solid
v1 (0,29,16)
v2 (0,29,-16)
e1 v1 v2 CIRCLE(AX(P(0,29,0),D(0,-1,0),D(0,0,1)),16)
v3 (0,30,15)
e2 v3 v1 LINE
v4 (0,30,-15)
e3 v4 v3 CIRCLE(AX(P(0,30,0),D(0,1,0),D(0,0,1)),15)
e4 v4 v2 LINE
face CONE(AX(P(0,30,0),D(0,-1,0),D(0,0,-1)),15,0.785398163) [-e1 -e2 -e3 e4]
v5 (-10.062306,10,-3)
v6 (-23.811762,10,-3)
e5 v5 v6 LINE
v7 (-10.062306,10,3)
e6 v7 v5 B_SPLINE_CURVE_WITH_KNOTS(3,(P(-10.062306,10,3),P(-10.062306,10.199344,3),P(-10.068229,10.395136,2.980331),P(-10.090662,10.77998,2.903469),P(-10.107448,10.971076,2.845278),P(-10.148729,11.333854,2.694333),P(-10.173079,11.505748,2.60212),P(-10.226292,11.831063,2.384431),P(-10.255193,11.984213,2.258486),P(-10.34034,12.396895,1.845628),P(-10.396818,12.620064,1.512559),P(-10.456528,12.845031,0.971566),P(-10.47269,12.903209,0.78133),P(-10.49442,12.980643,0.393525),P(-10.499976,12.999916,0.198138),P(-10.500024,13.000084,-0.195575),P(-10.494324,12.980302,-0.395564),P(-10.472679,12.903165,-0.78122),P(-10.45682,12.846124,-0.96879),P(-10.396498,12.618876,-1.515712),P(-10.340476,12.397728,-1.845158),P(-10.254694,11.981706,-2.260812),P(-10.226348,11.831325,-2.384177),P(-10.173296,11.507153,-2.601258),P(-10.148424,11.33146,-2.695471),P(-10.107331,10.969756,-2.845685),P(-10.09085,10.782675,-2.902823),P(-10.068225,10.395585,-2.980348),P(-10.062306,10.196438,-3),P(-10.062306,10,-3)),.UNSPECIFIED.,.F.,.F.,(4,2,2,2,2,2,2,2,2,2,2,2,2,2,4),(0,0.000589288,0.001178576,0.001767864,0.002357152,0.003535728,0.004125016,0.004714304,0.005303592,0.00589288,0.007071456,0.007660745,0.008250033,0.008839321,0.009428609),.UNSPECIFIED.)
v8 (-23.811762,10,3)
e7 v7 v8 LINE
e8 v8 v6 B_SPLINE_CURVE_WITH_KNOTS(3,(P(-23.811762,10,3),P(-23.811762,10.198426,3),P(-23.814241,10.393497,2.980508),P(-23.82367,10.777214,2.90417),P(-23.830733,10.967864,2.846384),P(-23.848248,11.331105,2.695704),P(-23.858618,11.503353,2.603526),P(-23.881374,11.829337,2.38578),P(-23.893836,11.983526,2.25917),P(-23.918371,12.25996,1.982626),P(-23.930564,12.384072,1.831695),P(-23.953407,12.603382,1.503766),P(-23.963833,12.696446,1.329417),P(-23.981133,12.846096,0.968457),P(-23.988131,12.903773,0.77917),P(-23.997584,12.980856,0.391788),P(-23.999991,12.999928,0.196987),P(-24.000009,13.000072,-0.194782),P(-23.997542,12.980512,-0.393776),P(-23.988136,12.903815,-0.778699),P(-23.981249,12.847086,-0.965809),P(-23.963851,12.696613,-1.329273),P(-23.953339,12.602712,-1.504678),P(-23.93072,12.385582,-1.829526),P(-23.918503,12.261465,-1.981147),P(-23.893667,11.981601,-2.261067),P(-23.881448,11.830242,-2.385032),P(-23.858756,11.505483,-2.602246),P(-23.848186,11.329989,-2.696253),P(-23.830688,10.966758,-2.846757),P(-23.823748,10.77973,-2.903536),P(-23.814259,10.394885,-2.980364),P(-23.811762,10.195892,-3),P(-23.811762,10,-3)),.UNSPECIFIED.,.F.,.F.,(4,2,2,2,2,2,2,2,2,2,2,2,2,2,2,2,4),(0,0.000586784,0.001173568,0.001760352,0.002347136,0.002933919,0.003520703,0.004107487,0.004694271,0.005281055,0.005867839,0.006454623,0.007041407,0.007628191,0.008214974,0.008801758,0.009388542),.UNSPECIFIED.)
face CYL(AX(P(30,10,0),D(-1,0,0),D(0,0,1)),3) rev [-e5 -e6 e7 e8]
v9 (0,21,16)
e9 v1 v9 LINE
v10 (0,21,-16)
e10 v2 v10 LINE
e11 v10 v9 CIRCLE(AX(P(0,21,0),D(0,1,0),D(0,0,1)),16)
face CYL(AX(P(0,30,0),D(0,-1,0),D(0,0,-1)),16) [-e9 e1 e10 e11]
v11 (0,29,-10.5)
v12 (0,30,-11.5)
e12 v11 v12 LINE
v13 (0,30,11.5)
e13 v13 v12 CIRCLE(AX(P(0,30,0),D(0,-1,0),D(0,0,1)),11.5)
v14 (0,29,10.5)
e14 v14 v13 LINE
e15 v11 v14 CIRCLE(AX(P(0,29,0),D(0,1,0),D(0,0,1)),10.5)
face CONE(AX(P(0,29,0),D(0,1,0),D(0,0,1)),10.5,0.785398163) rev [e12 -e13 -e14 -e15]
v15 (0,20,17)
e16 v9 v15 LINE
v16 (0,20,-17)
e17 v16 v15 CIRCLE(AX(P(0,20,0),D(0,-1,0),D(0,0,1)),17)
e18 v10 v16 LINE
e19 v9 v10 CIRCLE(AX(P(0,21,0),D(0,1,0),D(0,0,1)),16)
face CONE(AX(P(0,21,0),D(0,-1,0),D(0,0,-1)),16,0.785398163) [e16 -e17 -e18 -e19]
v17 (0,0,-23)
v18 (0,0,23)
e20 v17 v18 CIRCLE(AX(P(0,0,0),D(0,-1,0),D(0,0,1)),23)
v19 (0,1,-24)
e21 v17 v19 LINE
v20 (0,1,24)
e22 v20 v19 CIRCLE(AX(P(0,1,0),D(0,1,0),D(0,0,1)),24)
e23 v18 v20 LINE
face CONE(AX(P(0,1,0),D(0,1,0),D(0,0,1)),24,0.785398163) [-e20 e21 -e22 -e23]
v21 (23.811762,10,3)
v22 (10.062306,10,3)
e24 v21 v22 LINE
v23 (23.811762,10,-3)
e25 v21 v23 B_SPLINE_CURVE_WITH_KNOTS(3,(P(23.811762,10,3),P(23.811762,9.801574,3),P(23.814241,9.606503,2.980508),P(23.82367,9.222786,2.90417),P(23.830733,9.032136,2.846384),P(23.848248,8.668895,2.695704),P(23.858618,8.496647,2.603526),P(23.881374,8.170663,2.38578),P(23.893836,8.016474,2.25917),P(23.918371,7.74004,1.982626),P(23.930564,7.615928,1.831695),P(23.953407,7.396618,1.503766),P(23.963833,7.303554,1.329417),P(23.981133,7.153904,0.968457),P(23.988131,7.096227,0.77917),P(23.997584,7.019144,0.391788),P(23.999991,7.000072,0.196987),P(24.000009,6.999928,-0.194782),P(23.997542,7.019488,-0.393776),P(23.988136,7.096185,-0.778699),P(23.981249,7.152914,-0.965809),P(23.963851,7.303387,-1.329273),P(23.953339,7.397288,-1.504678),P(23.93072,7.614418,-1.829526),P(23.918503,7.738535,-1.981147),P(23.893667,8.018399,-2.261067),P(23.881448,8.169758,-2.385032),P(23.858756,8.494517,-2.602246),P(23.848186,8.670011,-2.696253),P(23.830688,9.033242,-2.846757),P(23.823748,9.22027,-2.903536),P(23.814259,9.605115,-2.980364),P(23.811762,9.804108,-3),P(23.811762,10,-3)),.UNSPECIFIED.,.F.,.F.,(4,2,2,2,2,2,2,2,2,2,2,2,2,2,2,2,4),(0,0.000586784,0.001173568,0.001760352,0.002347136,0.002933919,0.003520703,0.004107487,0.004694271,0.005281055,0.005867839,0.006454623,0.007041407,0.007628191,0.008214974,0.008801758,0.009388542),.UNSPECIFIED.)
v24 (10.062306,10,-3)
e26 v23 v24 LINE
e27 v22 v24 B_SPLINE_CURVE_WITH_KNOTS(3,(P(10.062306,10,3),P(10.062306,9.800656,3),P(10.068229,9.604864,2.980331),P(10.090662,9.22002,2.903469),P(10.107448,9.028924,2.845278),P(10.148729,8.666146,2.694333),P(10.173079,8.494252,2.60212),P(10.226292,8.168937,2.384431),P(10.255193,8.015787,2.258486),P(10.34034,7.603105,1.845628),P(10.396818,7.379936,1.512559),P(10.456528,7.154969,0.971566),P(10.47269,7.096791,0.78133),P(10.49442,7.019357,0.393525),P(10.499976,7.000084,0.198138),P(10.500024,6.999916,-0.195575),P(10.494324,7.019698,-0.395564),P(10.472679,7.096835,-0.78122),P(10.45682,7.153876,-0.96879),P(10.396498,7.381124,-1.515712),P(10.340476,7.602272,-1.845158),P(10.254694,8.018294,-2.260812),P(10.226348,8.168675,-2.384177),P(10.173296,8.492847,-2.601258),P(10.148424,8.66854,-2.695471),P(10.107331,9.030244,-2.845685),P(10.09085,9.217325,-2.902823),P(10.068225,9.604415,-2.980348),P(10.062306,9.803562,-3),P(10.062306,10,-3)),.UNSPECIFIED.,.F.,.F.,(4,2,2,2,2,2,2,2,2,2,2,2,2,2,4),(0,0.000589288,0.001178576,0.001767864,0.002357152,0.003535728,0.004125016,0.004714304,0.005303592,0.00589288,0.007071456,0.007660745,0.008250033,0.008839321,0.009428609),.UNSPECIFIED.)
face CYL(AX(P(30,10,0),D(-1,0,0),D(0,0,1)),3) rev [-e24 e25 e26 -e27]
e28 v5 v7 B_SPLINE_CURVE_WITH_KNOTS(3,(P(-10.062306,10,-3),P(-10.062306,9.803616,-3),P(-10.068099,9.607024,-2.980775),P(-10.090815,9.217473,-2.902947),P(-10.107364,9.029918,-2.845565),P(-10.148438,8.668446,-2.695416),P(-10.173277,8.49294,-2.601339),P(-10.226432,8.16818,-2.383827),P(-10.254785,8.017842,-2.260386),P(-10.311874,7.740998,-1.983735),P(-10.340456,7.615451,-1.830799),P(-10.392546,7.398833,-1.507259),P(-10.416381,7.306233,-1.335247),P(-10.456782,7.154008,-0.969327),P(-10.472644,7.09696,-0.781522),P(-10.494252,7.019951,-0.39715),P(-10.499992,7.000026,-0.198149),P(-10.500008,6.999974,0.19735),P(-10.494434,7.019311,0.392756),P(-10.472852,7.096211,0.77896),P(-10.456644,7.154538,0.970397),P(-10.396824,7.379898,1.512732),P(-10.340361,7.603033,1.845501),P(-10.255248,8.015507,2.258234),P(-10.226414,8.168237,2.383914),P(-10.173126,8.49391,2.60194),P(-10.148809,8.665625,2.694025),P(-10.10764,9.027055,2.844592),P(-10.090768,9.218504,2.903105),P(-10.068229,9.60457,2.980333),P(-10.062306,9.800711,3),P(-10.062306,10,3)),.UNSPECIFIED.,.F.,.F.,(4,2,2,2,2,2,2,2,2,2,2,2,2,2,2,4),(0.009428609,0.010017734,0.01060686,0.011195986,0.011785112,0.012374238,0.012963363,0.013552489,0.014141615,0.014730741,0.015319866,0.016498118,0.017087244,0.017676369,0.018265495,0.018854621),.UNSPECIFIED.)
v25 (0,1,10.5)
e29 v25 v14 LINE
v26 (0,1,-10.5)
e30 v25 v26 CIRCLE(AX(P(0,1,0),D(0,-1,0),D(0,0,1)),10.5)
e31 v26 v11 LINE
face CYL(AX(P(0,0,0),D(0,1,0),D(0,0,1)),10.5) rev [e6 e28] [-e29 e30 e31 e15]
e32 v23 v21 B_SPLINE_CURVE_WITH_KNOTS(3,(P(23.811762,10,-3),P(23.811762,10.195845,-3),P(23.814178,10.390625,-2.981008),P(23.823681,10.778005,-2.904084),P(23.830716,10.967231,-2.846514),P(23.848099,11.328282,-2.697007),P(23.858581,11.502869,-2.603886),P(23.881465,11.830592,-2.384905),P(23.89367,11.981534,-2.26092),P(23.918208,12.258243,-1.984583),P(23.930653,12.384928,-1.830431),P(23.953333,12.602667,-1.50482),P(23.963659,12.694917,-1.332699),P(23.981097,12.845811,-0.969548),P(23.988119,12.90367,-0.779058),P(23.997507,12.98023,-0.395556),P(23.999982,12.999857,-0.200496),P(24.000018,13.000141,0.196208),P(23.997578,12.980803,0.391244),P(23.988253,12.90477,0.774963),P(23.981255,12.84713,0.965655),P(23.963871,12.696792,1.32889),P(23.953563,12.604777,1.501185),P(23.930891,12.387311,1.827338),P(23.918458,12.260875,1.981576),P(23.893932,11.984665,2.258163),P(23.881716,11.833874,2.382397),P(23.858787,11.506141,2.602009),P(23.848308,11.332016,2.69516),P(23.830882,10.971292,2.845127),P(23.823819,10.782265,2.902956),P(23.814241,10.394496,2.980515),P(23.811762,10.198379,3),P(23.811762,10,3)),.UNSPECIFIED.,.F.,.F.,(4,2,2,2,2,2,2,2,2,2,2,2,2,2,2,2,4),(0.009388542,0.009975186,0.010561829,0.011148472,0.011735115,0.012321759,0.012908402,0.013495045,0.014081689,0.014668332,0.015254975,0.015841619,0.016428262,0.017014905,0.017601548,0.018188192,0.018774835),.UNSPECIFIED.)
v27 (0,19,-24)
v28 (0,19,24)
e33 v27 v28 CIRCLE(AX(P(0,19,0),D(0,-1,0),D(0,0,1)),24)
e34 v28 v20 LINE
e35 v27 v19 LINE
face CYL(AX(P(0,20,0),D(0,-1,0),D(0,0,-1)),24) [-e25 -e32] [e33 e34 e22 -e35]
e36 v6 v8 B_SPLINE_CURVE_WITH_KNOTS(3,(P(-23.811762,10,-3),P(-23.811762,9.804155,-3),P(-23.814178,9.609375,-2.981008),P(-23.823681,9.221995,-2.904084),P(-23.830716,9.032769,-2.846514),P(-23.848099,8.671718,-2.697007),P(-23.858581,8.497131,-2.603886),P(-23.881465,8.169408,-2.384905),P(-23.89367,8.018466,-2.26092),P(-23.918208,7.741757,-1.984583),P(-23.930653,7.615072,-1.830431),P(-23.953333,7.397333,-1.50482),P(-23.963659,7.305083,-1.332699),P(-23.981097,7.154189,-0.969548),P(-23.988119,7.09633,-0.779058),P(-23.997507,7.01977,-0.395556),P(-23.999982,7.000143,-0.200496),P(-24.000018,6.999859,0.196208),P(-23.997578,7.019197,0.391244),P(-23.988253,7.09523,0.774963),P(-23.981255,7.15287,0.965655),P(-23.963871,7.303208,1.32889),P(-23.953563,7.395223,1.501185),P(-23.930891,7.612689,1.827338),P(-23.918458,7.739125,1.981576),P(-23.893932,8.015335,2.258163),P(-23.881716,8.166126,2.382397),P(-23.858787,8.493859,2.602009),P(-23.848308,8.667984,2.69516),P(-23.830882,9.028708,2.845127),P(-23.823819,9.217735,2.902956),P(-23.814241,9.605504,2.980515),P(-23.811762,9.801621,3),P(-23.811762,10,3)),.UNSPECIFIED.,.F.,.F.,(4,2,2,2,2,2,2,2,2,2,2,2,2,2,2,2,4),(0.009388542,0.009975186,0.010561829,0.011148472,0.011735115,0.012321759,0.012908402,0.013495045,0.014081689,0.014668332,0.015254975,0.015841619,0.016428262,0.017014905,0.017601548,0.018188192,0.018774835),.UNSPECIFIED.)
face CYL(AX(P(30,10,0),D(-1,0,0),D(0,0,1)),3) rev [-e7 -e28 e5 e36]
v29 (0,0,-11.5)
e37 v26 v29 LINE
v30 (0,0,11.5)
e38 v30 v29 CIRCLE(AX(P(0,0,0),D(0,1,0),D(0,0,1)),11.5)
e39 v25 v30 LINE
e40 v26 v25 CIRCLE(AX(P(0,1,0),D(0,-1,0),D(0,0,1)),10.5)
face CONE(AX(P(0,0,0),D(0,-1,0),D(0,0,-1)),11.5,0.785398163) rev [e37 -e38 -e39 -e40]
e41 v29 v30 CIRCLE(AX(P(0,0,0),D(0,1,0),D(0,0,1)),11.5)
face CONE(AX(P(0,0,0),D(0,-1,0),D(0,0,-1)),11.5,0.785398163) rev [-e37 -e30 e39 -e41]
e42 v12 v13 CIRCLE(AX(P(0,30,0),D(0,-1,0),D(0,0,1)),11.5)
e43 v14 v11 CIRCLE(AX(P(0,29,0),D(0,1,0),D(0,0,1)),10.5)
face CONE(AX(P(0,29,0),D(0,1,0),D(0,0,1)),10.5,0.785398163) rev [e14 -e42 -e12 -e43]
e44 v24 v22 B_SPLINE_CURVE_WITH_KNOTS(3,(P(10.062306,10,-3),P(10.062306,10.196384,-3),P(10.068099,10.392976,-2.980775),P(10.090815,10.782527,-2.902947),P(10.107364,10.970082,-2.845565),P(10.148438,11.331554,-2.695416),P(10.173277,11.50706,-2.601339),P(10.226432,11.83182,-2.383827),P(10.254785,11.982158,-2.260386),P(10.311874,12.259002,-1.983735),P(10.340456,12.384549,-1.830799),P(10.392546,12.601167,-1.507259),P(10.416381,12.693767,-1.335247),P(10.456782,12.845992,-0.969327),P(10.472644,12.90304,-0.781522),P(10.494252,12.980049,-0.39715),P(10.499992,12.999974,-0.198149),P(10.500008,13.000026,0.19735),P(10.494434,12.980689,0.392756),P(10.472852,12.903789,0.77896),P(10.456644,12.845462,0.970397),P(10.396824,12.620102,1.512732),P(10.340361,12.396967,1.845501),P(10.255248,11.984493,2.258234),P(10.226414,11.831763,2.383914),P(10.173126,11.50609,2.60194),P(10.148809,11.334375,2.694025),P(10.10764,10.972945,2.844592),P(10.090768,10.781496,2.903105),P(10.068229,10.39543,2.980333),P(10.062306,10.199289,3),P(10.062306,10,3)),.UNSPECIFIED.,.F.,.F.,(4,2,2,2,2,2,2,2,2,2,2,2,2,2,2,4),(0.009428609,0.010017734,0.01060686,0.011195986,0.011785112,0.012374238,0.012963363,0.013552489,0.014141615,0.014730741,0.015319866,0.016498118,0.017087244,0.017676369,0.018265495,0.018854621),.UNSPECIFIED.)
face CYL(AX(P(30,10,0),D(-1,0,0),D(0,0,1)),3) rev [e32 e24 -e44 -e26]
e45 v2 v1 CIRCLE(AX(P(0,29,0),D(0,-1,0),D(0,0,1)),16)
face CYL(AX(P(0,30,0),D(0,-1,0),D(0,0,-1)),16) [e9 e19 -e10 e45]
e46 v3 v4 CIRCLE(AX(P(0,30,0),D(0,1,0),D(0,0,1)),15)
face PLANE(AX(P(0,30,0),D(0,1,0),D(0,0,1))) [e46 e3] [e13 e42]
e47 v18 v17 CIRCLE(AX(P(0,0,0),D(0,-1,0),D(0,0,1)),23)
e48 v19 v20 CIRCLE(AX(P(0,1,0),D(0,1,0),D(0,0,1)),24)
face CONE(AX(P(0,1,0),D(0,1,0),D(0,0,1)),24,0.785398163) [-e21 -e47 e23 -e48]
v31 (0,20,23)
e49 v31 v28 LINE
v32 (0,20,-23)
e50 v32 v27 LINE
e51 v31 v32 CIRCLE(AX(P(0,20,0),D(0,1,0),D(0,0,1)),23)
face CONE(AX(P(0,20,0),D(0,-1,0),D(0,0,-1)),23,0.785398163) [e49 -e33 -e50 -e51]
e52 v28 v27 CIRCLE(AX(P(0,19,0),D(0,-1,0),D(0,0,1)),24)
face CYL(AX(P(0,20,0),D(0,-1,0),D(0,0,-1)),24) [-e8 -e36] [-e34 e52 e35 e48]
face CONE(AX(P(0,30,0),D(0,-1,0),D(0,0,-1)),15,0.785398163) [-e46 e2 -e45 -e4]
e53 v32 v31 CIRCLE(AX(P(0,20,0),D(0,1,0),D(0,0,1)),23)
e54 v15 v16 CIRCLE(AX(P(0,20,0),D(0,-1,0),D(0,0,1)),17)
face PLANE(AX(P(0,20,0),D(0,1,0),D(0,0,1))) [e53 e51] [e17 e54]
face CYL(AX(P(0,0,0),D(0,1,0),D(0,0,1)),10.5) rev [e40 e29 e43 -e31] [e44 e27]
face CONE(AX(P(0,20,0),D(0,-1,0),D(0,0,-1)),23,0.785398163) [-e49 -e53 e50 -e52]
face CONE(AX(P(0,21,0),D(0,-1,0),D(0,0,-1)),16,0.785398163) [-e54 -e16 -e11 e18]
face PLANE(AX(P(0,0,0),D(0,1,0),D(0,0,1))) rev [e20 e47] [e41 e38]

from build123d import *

# Parameters (mm, degrees)
SKETCH1_R               = 24
BOSS_EXTRUDE1_DEPTH     = 20
CUT_EXTRUDE2_DEPTH      = 30
CUT_EXTRUDE2_DEPTH_BACK = 30
SKETCH3_R               = 3
SKETCH4_R               = 16
BOSS_EXTRUDE2_DEPTH     = 10
SKETCH5_R               = 10.5
CUT_EXTRUDE3_DEPTH      = 30
CHAMFER1_SIZE           = 1
CHAMFER2_SIZE           = 1


with BuildPart() as part:
    # Sketch1 → Boss-Extrude1 (new body)
    with BuildSketch(Plane(origin=(0, 0, 0), x_dir=(1, 0, 0), z_dir=(0, 1, 0))):
        with Locations(Location((0, 0, 0), (0, 0, 270))):
            Circle(SKETCH1_R)
    extrude(amount=BOSS_EXTRUDE1_DEPTH)

    # Sketch3 → Cut-Extrude2 (cut, two sides: drawn at the far end of the back side and taken through both)
    with BuildSketch(Plane(origin=(0, 0, 0), x_dir=(0, 0, -1), z_dir=(1, 0, 0)).offset(-CUT_EXTRUDE2_DEPTH_BACK)):
        with Locations(Location((0, 10, 0), (0, 0, 180))):
            Circle(SKETCH3_R)
    extrude(amount=CUT_EXTRUDE2_DEPTH + CUT_EXTRUDE2_DEPTH_BACK, mode=Mode.SUBTRACT)

    # Sketch4 → Boss-Extrude2 (add)
    with BuildSketch(Plane(origin=(0, 20, 0), x_dir=(1, 0, 0), z_dir=(0, 1, 0))):
        with Locations(Location((0, 0, 0), (0, 0, 270))):
            Circle(SKETCH4_R)
    extrude(amount=BOSS_EXTRUDE2_DEPTH)

    # Sketch5 → Cut-Extrude3 (cut)
    with BuildSketch(Plane(origin=(0, 30, 0), x_dir=(1, 0, 0), z_dir=(0, 1, 0))):
        with Locations(Location((0, 0, 0), (0, 0, 270))):
            Circle(SKETCH5_R)
    extrude(amount=-CUT_EXTRUDE3_DEPTH, mode=Mode.SUBTRACT)

    # Chamfer1
    chamfer1_edges = [part.edges().sort_by_distance(p)[0] for p in [
        (0, 20, -16),
        (0, 30, -16),
        (0, 0, -10.5),
        (0, 0, -24),
        (0, 20, -24),
    ]]
    chamfer(chamfer1_edges, length=CHAMFER1_SIZE)

    # Chamfer2
    chamfer2_edges = [part.edges().sort_by_distance(p)[0] for p in [
        (0, 30, -10.5),
    ]]
    chamfer(chamfer2_edges, length=CHAMFER2_SIZE)


solid = part.part
